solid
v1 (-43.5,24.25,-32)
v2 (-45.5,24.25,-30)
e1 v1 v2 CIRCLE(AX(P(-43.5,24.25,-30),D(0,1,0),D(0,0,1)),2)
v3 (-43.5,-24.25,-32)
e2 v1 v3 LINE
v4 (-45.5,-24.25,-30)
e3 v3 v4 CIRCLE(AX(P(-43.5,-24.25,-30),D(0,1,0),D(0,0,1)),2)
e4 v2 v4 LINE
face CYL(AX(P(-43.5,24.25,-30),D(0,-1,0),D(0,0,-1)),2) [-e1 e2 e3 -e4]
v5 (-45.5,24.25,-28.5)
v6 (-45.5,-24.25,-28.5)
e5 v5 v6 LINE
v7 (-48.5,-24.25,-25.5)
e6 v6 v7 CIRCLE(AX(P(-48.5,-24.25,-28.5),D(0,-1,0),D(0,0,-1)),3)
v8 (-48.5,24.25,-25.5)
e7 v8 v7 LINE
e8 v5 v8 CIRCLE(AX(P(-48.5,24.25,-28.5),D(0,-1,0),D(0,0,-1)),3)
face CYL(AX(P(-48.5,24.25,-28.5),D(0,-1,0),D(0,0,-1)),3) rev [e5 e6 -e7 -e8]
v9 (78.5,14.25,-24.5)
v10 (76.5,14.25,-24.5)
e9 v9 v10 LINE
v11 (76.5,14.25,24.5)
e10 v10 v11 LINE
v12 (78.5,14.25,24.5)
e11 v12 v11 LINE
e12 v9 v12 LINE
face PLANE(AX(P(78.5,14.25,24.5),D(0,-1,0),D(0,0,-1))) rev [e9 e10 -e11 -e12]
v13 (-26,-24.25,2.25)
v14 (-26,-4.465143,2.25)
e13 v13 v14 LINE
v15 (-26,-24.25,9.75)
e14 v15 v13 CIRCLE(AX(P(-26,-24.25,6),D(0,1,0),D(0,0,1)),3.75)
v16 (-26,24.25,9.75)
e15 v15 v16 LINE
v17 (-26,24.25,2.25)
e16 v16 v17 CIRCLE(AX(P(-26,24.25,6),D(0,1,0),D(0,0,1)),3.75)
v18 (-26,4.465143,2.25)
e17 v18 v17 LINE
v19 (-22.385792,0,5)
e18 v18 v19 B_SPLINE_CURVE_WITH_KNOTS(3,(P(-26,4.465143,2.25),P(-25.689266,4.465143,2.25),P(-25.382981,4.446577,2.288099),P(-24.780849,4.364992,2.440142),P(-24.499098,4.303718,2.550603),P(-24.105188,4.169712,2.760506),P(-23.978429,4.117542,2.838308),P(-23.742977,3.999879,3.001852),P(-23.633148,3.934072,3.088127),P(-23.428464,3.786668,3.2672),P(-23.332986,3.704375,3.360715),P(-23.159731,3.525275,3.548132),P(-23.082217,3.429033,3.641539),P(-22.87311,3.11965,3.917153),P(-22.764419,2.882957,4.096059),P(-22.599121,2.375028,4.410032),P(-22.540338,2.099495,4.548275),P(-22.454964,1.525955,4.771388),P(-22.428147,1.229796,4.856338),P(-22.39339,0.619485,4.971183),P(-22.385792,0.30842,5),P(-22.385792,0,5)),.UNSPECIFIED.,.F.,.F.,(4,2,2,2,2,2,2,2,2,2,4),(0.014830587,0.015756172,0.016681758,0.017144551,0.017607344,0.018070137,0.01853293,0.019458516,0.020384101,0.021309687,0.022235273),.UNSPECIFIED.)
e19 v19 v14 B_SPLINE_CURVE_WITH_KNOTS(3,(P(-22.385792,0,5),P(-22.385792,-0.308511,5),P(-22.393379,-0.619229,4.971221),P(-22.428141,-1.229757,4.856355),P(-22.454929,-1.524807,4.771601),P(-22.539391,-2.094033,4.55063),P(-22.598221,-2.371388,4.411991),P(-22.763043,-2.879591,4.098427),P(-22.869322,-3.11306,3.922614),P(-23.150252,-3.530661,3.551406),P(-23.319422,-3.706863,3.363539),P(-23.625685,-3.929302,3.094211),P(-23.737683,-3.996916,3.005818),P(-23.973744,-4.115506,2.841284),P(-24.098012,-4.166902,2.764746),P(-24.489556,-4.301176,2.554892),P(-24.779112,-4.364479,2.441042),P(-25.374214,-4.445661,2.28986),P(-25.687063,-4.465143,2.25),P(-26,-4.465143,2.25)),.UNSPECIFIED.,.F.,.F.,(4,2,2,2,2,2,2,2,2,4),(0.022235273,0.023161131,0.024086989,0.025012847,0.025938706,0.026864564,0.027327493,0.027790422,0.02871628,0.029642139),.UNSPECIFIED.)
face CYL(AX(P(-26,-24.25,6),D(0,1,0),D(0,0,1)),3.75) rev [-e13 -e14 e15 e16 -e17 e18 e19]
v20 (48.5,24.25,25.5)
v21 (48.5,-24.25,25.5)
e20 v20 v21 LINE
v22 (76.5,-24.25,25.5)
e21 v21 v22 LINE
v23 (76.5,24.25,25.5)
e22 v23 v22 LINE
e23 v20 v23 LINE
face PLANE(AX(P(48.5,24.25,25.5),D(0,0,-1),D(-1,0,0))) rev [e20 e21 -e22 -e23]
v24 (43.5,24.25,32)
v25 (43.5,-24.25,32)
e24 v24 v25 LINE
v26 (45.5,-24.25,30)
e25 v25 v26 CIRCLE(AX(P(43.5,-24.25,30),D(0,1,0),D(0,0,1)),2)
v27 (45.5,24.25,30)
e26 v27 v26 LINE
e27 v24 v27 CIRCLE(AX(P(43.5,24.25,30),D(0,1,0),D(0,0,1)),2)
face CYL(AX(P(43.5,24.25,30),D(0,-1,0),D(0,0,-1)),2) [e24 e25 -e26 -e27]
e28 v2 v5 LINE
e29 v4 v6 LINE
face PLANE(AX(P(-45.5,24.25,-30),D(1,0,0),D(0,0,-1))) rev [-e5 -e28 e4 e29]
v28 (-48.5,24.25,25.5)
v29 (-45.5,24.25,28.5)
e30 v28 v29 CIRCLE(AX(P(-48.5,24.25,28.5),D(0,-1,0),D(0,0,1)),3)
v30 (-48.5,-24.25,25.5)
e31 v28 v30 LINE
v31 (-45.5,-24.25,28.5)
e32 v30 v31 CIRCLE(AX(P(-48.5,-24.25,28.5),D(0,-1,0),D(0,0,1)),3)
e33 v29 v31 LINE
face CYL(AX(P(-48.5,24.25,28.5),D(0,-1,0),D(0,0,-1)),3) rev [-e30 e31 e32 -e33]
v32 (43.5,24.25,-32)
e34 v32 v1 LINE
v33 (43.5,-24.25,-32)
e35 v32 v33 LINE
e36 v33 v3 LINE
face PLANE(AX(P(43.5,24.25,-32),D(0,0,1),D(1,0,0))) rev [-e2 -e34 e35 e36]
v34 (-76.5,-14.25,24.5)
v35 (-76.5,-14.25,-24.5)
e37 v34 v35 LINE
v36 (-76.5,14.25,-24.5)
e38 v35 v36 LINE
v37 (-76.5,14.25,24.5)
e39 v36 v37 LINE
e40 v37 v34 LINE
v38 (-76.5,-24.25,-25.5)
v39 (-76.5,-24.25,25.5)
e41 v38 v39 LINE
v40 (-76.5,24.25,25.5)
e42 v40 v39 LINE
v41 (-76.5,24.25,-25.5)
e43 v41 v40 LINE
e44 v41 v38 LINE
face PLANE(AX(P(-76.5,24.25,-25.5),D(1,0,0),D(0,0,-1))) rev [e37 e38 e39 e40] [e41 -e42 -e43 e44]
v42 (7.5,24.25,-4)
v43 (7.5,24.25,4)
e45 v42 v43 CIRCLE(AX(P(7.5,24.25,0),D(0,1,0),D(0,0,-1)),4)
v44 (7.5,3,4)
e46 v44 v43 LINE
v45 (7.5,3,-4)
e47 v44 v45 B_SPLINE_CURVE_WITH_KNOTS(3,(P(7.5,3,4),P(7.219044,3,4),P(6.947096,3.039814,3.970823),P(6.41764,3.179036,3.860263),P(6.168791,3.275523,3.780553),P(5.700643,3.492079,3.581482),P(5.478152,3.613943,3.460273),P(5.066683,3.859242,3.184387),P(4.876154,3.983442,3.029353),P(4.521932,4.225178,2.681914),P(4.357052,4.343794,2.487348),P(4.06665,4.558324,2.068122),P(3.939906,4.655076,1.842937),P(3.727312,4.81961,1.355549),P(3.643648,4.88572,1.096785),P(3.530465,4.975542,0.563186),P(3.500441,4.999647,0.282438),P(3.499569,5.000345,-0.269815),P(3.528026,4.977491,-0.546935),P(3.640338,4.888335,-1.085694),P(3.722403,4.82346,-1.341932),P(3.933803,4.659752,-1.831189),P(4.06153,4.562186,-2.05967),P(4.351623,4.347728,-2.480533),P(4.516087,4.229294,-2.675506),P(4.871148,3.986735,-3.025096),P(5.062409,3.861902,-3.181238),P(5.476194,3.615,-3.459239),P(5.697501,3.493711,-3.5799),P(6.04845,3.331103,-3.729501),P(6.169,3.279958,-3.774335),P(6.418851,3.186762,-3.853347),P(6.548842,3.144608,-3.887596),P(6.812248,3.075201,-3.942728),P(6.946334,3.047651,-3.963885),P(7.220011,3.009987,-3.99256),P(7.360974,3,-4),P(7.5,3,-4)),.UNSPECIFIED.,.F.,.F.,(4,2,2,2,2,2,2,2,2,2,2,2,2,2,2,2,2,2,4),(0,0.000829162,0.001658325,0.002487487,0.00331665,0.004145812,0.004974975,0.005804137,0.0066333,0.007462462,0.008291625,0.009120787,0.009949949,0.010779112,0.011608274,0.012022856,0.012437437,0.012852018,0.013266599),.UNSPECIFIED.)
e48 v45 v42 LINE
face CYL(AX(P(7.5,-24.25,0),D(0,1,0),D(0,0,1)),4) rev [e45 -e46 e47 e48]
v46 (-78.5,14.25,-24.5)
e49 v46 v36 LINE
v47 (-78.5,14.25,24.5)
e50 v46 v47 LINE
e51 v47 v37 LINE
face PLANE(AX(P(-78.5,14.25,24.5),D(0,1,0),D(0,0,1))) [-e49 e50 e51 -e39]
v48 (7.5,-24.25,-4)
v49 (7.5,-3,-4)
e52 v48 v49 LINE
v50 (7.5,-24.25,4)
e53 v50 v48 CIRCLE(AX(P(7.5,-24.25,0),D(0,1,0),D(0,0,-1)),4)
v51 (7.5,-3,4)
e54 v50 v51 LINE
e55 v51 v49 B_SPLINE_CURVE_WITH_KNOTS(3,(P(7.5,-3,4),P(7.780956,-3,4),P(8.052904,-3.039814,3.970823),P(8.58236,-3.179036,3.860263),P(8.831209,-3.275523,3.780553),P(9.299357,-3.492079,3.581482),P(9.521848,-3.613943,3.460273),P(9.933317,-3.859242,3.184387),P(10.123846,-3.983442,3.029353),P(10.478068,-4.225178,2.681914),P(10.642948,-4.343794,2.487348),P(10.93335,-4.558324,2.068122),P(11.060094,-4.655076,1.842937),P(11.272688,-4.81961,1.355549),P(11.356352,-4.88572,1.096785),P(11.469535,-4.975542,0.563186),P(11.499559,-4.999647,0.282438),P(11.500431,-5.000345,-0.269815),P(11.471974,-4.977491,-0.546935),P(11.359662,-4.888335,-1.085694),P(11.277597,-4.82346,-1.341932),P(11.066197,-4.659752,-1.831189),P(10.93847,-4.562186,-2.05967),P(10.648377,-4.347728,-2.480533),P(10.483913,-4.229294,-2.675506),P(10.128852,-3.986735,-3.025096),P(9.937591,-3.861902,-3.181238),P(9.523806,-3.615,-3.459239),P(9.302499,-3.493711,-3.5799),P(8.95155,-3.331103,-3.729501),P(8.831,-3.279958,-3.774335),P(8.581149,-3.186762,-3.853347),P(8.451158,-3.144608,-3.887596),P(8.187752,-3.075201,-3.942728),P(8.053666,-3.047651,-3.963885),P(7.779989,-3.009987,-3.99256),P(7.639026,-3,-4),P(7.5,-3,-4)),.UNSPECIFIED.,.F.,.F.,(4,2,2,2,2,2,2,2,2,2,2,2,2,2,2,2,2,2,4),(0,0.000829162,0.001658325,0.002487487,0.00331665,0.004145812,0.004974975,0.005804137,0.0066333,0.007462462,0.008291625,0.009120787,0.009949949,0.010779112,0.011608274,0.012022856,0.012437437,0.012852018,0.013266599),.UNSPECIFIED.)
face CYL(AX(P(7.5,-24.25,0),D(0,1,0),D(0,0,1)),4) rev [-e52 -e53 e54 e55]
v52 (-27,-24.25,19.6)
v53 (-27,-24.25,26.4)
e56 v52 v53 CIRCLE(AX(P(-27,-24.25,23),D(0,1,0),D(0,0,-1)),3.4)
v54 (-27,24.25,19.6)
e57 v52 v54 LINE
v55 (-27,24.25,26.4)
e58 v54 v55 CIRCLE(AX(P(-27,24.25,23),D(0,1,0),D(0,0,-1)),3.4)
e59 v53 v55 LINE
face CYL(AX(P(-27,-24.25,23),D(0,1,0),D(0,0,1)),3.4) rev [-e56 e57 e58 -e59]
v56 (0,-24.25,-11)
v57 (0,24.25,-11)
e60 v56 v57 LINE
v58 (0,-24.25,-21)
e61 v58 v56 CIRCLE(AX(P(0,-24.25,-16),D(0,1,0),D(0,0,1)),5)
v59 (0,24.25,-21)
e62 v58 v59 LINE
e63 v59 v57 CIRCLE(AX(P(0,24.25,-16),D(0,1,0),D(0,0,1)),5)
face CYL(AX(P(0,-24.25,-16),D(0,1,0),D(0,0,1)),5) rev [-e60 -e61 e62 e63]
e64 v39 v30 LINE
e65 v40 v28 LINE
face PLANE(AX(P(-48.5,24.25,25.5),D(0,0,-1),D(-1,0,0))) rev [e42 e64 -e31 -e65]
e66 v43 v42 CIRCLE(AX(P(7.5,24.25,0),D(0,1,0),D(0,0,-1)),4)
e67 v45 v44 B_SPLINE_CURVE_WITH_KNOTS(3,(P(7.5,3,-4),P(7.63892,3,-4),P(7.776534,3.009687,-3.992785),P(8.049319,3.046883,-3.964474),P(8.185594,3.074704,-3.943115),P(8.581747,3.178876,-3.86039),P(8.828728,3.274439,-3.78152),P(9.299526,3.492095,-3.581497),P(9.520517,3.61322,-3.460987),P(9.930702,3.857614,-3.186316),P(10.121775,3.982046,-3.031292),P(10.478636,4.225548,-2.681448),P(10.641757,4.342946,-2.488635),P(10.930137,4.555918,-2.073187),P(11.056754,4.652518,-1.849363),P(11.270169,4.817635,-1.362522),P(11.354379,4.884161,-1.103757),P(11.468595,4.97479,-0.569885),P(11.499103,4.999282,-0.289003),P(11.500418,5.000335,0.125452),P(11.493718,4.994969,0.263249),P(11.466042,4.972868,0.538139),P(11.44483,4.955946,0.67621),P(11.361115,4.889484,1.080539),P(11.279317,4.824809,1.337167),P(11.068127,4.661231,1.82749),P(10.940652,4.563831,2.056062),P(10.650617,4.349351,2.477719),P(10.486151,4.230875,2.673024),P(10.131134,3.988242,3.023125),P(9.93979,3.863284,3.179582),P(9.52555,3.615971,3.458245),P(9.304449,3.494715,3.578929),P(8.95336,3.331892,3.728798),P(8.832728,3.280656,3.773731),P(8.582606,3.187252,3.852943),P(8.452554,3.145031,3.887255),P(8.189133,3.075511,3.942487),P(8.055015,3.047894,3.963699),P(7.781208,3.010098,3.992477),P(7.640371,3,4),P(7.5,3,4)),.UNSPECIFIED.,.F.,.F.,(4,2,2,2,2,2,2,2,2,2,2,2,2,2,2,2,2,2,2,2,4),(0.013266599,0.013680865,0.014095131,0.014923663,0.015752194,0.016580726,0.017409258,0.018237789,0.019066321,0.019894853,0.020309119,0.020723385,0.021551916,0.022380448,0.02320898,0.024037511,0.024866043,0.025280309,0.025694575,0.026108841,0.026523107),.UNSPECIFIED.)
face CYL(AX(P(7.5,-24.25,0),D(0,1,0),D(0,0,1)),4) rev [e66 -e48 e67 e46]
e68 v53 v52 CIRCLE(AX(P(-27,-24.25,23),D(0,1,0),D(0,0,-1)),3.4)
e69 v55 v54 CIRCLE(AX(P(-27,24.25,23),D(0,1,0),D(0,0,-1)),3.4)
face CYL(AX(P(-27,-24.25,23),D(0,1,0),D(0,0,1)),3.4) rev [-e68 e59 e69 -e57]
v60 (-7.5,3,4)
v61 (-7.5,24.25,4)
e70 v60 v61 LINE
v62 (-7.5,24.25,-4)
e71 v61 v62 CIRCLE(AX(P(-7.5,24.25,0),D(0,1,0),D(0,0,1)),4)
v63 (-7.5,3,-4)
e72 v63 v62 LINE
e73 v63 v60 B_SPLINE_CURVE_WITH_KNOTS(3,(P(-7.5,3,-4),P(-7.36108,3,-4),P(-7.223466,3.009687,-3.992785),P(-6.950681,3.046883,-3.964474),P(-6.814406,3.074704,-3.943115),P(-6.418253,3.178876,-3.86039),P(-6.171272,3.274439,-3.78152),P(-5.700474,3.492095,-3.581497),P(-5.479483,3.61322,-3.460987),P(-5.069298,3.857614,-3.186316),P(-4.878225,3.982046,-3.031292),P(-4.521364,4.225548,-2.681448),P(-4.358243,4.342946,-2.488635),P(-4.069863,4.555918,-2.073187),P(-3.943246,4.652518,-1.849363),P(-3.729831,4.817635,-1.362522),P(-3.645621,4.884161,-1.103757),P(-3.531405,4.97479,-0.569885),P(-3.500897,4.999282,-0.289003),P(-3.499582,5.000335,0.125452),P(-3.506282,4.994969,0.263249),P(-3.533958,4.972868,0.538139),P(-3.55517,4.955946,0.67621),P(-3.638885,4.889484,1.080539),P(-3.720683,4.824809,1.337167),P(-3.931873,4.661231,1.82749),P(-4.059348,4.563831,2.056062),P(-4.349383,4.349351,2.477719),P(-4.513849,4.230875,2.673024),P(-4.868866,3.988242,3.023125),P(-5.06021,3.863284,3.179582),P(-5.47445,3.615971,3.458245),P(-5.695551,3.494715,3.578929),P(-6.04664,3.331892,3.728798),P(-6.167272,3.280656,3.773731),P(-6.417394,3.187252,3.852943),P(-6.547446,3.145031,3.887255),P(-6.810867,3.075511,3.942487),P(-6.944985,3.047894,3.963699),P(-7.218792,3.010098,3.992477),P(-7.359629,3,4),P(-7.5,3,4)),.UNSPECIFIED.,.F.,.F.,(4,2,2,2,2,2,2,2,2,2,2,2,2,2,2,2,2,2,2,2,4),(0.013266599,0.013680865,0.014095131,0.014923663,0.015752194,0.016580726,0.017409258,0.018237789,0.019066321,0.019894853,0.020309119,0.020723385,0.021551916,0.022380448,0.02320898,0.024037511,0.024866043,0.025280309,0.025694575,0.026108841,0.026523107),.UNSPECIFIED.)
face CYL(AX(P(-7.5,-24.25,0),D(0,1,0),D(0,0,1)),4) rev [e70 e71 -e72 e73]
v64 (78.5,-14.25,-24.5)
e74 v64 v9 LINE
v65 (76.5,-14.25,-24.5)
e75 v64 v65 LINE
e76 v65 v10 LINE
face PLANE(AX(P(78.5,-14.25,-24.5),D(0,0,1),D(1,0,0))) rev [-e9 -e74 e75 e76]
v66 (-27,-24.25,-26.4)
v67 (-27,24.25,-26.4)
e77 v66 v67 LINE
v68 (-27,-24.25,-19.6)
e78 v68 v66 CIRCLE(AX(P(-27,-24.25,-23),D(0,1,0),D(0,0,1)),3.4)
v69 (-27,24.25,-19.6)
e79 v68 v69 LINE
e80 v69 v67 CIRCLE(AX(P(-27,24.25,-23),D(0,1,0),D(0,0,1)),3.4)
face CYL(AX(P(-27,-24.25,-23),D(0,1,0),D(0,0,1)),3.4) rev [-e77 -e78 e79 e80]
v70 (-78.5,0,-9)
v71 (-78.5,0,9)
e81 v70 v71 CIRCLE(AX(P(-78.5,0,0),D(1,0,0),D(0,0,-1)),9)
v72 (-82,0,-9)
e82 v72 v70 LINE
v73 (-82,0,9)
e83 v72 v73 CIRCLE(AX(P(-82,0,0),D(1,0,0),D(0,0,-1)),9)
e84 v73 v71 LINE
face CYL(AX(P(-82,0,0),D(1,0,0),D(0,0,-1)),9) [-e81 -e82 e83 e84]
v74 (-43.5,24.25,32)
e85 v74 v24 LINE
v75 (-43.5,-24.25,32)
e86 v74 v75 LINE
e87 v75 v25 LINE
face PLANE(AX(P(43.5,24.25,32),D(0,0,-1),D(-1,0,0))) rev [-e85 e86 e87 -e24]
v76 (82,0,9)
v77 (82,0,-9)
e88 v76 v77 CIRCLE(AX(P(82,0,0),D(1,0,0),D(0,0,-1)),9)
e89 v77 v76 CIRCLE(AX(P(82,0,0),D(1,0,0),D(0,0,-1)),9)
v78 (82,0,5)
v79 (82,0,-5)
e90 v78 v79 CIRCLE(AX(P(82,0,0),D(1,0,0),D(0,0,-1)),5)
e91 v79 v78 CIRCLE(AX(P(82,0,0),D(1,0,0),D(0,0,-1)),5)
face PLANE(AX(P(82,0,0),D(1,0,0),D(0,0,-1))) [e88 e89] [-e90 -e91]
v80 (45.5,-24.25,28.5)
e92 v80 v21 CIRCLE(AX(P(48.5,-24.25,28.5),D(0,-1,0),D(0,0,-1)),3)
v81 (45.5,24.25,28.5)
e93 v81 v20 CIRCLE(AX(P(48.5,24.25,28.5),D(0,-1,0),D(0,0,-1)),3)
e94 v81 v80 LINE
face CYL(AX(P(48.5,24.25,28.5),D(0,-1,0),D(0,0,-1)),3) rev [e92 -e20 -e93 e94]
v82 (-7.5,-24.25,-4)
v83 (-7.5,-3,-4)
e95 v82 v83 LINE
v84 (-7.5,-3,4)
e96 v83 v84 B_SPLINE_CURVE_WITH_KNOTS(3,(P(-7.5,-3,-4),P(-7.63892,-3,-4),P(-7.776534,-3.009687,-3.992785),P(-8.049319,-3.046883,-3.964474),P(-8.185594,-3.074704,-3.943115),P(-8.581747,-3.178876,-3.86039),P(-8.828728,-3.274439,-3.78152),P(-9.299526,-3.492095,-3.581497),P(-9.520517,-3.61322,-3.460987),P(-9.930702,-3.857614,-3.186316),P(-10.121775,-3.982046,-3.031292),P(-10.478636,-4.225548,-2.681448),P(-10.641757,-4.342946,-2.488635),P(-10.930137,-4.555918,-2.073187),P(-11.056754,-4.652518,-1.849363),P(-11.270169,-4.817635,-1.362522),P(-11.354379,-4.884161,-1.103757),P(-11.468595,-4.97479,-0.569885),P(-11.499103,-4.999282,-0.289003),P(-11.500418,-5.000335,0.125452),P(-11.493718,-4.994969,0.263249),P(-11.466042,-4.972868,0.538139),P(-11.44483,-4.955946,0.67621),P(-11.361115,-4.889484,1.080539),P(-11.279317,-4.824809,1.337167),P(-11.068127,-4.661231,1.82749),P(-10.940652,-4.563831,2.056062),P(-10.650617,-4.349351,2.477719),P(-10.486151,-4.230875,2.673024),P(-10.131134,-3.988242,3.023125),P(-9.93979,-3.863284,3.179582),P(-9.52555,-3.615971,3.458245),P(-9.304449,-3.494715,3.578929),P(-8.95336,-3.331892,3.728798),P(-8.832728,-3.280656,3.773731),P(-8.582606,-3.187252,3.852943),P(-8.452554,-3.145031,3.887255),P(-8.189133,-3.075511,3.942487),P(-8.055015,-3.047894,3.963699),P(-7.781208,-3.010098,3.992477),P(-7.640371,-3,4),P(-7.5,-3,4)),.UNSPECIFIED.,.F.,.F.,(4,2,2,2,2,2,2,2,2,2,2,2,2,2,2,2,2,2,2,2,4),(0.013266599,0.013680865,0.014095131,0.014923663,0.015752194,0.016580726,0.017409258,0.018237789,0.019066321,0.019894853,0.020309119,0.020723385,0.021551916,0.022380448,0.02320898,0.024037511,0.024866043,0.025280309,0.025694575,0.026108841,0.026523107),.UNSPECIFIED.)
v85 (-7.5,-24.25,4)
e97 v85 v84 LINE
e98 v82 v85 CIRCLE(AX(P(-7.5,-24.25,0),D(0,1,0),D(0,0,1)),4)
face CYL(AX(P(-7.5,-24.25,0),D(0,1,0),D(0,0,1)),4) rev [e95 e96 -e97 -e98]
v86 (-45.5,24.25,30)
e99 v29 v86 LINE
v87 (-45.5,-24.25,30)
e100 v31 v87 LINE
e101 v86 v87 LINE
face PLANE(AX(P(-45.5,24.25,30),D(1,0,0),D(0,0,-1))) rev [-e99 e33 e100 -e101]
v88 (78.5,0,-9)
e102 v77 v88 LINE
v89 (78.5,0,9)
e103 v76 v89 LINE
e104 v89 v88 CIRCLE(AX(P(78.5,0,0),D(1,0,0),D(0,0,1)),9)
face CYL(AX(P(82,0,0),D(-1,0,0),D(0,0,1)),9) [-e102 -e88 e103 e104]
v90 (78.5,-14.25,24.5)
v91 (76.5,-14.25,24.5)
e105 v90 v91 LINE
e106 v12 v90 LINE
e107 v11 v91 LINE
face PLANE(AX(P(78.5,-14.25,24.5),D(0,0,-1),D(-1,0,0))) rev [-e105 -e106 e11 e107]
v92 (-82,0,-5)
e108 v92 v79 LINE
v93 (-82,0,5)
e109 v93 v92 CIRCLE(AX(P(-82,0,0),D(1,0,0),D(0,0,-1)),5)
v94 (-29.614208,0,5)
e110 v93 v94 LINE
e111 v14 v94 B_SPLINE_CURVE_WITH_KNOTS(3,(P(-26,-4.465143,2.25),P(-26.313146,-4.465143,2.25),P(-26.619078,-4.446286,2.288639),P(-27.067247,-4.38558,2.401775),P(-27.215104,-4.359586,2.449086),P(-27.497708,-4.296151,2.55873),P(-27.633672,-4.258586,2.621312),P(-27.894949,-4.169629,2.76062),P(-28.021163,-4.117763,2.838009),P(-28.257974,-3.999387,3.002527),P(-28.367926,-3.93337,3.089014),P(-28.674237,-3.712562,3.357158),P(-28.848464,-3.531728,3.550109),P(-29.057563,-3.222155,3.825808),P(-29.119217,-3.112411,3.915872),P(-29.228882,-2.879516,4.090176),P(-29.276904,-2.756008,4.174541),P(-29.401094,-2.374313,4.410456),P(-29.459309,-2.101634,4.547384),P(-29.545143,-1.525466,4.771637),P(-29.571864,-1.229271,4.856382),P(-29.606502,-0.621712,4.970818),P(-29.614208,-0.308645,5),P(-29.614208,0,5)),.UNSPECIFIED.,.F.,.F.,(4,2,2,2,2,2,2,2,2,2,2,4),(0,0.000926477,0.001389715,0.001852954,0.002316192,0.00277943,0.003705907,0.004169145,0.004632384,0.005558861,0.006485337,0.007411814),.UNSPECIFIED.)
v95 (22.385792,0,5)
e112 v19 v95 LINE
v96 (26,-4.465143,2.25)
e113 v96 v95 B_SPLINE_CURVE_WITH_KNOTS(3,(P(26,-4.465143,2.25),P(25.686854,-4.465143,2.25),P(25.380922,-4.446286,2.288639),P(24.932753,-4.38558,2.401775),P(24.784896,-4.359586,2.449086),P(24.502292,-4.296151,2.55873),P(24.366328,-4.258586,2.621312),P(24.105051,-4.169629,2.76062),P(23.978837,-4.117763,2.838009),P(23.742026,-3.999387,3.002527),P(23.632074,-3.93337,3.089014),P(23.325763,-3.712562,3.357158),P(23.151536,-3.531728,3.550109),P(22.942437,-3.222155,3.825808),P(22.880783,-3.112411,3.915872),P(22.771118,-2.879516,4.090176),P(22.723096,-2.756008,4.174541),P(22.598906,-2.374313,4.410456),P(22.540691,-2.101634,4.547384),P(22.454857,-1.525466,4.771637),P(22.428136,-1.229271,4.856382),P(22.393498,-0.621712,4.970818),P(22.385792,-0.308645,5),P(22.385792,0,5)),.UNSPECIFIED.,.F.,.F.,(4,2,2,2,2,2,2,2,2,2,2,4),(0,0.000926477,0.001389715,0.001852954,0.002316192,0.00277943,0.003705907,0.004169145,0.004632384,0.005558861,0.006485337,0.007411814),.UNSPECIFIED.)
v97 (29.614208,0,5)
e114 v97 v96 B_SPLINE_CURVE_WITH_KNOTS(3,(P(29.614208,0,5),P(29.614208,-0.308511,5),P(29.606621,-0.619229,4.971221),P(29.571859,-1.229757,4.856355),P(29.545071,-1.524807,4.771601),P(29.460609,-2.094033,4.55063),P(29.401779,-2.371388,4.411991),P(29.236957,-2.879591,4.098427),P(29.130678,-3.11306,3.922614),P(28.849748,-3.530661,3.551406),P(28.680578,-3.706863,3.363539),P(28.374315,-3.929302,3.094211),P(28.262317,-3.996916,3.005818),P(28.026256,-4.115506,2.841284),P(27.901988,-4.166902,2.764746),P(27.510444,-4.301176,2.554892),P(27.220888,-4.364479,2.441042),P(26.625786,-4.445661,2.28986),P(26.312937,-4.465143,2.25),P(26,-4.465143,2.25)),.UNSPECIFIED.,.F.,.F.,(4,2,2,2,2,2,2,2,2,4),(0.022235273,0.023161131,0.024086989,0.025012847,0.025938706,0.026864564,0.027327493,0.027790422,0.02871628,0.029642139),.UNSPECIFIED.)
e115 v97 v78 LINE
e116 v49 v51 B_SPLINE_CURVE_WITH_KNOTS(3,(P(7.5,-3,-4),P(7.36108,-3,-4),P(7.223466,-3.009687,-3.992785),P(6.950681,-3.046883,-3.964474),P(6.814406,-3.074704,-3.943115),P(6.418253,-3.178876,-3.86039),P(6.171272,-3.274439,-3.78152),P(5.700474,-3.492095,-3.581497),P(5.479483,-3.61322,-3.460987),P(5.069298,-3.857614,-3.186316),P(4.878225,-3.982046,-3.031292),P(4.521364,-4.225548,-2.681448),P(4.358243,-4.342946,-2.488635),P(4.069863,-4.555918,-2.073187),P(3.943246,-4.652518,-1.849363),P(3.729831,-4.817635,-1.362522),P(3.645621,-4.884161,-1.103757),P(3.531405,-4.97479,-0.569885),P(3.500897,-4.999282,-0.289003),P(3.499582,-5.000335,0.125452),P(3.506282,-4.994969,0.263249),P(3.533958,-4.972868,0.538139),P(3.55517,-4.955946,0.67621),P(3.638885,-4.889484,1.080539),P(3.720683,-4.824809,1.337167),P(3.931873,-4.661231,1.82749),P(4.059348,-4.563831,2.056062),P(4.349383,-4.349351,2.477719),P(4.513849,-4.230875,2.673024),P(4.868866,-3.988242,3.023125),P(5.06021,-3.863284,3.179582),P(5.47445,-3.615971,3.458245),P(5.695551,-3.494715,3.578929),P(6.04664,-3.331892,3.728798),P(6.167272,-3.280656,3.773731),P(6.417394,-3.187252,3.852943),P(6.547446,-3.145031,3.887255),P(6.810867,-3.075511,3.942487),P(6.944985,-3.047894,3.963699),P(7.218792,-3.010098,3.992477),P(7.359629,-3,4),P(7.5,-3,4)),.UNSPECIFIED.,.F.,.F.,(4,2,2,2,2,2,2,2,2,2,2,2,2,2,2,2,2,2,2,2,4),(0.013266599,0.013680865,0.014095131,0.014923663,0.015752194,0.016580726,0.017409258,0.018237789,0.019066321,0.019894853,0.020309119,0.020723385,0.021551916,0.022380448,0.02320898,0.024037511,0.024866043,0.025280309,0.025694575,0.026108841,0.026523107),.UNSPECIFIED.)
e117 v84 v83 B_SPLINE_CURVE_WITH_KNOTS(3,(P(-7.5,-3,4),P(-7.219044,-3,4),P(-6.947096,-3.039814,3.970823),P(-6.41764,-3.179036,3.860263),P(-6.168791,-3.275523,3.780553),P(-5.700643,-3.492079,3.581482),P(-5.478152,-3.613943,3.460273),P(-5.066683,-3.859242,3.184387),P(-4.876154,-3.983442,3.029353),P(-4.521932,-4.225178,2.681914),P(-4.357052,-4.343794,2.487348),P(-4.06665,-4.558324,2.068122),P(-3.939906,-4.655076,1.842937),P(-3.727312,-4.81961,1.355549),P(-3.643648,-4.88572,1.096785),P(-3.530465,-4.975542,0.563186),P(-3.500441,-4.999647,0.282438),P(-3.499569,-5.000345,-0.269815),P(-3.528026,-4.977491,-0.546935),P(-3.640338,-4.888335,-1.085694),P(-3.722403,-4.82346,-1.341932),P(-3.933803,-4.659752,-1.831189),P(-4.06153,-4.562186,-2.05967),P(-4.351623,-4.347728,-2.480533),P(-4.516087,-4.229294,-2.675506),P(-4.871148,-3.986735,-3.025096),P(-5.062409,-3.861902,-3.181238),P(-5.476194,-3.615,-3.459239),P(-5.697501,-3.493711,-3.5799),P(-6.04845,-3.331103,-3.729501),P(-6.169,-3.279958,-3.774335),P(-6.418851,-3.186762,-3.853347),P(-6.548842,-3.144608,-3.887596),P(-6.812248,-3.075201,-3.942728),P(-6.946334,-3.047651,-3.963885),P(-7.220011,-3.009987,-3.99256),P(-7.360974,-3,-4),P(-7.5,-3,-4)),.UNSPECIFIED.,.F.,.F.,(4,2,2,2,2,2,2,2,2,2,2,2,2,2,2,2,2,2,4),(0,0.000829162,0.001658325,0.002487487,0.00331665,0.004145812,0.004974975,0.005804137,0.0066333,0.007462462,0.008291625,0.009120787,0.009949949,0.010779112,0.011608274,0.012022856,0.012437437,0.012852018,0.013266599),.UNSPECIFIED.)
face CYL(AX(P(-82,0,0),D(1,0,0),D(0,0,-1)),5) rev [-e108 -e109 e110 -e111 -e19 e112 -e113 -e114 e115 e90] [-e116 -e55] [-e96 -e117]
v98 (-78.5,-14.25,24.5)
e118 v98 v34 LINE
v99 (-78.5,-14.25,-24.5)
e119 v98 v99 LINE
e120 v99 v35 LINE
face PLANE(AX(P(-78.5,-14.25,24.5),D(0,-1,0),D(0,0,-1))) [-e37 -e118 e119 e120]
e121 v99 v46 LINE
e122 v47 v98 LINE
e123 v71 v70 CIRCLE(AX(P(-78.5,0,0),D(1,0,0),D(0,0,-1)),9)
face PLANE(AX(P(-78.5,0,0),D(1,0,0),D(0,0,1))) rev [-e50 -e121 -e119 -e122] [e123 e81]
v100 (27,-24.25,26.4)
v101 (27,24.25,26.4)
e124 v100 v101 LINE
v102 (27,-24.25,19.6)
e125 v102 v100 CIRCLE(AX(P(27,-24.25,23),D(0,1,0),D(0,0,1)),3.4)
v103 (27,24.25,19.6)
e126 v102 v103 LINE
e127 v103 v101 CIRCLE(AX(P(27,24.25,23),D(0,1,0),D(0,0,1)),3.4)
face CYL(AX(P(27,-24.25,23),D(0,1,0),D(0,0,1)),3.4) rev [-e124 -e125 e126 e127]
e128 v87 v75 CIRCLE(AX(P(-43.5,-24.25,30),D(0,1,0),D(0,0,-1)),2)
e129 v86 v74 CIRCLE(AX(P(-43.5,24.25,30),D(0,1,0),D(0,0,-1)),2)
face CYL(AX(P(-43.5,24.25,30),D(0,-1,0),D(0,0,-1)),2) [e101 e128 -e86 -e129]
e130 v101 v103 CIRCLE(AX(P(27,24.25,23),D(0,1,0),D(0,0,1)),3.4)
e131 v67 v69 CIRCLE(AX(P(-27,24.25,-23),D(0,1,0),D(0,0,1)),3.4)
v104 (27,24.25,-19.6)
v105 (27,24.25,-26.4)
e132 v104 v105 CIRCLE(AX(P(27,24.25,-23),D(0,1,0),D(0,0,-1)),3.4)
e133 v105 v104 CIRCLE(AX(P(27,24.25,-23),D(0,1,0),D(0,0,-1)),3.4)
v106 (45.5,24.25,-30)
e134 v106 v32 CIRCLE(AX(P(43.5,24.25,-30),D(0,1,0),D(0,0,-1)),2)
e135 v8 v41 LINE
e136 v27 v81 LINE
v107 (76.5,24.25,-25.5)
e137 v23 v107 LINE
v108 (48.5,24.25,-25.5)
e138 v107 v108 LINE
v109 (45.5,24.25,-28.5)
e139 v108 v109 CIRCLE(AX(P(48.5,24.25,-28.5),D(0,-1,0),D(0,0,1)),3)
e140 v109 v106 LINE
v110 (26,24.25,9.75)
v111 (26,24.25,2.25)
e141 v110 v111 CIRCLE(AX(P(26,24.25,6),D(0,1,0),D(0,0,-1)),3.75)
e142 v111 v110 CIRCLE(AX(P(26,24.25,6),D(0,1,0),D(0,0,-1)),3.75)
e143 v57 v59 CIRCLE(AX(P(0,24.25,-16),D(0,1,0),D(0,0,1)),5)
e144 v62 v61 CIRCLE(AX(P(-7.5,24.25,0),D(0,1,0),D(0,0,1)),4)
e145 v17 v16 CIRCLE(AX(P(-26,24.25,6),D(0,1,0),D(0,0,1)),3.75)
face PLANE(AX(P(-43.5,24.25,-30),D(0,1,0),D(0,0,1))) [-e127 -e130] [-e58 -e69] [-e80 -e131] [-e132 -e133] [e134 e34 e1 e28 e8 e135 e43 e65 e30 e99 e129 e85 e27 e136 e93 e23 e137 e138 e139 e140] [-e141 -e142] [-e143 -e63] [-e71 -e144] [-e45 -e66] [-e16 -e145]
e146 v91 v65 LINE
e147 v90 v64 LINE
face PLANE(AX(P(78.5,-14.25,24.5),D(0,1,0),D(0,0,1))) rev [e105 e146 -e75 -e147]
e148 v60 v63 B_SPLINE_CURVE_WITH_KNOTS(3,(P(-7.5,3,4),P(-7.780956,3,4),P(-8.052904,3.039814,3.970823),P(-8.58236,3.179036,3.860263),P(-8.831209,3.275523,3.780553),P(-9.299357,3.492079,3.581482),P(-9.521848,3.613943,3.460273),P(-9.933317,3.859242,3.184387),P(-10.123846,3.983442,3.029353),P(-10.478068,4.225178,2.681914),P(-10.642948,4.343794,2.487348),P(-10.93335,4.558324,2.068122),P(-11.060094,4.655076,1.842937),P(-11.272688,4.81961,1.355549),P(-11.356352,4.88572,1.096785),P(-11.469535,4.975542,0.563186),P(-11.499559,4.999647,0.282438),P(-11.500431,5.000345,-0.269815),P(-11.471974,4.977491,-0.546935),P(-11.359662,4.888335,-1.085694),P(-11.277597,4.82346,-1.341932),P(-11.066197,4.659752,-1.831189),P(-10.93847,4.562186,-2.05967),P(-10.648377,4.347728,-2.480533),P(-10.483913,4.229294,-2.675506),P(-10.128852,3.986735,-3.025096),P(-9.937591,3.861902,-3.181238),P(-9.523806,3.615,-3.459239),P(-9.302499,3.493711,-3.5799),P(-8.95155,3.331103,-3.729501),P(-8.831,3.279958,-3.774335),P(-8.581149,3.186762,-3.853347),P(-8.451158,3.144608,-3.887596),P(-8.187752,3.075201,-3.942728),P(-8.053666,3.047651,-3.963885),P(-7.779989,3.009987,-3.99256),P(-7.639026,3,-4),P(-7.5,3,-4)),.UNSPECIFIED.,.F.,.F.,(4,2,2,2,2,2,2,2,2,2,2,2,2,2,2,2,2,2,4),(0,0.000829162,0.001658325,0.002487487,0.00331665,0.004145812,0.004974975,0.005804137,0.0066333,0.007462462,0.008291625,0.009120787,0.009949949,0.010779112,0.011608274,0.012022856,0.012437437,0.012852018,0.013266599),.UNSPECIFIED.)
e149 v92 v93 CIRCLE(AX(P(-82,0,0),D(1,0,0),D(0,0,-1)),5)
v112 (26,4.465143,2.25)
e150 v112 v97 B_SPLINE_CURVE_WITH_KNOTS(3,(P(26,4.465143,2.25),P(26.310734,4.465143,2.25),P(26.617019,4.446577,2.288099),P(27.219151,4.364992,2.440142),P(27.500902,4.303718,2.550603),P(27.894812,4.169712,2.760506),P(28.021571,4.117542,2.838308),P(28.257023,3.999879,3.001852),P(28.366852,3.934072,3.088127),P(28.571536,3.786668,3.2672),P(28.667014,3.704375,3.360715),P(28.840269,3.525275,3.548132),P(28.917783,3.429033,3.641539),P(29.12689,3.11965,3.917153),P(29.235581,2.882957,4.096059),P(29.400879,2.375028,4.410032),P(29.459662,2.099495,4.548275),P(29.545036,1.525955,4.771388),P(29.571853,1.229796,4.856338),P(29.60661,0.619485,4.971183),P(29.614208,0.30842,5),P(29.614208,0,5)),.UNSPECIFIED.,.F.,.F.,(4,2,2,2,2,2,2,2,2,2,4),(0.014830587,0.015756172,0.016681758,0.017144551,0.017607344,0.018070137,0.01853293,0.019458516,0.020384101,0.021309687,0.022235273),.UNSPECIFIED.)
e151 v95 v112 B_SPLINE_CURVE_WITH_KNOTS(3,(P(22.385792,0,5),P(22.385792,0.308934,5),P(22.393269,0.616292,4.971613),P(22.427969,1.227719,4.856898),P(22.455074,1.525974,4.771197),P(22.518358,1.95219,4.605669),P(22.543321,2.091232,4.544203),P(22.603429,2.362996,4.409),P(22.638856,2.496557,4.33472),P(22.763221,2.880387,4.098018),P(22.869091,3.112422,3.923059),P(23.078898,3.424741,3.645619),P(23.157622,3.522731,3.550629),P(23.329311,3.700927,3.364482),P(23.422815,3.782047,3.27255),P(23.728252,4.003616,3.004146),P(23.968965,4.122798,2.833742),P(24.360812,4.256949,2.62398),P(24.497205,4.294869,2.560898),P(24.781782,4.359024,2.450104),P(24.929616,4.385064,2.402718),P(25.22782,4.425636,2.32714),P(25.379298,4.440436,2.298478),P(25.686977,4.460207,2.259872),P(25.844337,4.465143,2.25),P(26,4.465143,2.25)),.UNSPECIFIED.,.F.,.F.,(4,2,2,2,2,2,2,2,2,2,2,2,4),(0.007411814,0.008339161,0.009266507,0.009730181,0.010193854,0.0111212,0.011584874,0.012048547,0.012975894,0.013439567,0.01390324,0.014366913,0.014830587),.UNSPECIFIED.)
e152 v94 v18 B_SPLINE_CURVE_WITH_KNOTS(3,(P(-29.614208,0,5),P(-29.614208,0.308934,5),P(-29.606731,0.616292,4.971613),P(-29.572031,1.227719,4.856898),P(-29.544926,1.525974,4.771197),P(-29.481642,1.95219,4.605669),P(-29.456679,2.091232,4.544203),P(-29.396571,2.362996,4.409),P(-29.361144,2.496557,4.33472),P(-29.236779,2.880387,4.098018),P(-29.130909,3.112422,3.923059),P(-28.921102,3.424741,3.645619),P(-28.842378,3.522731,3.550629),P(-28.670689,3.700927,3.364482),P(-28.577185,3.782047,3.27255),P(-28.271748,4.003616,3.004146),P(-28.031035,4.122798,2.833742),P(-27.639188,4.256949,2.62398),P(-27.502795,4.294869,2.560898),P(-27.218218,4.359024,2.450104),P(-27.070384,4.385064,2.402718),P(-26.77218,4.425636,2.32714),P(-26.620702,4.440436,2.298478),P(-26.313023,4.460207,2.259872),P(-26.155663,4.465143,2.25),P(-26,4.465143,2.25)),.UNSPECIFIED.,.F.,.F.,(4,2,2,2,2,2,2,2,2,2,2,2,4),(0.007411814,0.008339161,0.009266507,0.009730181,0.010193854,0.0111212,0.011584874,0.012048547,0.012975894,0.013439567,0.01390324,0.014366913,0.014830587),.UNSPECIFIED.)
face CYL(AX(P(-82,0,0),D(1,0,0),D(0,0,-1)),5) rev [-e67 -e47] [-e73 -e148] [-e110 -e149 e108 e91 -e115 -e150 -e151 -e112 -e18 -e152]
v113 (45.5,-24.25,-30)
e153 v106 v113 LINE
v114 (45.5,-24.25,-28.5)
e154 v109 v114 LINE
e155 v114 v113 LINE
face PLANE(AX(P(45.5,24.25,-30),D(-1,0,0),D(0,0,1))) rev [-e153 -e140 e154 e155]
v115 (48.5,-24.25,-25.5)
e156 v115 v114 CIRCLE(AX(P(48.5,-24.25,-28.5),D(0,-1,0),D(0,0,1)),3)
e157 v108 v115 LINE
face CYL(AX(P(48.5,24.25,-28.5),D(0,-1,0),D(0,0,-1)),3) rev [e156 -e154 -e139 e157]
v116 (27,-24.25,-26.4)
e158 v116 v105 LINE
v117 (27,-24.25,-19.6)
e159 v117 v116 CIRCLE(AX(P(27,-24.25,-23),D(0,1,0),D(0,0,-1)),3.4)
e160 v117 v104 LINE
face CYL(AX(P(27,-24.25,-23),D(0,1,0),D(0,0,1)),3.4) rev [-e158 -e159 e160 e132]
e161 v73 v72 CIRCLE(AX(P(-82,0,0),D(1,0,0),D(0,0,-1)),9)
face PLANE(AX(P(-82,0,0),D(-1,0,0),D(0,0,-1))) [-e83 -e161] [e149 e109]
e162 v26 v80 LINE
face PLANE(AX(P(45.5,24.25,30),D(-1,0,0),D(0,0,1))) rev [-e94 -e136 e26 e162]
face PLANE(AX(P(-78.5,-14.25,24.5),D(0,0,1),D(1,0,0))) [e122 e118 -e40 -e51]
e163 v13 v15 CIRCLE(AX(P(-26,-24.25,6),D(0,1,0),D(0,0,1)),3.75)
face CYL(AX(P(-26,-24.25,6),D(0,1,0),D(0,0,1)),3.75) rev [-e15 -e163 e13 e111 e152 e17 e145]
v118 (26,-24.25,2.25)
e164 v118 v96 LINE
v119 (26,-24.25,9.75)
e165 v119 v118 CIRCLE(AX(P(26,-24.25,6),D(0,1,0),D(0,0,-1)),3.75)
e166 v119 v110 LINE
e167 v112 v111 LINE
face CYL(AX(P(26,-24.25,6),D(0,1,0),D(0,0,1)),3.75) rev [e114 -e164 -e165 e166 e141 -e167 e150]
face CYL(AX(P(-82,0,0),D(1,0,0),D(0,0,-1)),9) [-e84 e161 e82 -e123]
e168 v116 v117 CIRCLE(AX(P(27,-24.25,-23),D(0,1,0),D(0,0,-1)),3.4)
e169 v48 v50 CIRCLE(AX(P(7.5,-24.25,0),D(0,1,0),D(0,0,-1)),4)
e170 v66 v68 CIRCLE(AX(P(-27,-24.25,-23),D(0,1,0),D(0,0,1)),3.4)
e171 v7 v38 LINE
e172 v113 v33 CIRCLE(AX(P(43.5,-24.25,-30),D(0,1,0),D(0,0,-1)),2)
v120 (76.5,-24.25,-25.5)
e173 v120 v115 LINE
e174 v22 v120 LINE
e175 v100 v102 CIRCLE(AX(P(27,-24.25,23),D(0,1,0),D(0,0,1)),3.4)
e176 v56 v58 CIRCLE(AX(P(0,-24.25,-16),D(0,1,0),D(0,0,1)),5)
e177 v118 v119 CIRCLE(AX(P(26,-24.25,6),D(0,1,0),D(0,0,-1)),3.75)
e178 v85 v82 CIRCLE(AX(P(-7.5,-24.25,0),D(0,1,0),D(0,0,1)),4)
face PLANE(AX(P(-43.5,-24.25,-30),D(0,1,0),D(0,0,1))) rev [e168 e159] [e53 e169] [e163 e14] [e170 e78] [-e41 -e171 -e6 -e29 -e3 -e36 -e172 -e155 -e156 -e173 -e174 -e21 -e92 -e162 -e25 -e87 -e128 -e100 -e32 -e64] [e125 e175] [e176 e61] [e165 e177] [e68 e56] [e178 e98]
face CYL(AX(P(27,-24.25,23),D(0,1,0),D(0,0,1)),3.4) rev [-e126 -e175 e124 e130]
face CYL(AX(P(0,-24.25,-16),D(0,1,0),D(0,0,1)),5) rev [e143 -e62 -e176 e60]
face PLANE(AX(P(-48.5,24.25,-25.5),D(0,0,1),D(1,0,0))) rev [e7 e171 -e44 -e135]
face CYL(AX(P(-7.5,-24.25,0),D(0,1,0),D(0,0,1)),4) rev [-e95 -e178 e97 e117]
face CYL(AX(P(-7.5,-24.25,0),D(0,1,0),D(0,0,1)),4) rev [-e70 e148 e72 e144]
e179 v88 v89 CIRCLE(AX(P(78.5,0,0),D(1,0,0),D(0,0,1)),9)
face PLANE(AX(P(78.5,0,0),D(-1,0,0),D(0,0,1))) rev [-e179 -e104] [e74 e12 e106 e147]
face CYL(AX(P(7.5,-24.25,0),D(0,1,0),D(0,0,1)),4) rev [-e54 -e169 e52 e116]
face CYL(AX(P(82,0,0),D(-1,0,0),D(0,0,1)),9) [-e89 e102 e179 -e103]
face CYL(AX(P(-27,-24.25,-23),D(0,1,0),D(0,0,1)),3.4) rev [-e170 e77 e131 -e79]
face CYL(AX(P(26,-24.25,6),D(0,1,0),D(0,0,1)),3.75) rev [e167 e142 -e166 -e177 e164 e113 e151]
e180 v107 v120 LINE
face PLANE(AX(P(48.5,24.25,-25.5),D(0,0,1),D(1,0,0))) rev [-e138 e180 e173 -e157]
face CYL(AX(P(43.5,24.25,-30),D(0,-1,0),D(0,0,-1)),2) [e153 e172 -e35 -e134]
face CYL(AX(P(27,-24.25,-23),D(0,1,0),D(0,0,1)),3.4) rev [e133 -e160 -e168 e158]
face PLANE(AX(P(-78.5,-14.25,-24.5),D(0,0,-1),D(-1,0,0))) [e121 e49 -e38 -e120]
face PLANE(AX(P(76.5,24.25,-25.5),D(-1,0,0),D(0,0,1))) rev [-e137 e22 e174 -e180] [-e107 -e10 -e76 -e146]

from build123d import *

# Parameters (mm, degrees)
BOSS_EXTRUDE_1_DEPTH = 24.25
SKETCH_2_W           = 49
SKETCH_2_H           = 28.5
SKETCH_2_R           = 3.024345666
BOSS_EXTRUDE_2_DEPTH = 2
SKETCH_3_R           = 9
BOSS_EXTRUDE_3_DEPTH = 5.5
SKETCH_4_R           = 3.4
SKETCH_4_R_2         = 5
SKETCH_4_R_3         = 4
SKETCH_4_R_4         = 3.75
CUT_EXTRUDE_1_DEPTH  = 101.5
SKETCH_5_R           = 5
CUT_EXTRUDE_2_DEPTH  = 169.843307537


with BuildPart() as part:
    # Sketch 1 → Boss-Extrude 1 (new, symmetric)
    with BuildSketch(Plane(origin=(0, 0, 0), x_dir=(1, 0, 0), z_dir=(0, 1, 0))):
        with BuildLine():
            Line((43.5, 32), (-43.5, 32))
            ThreePointArc((-43.5, 32), (-44.914213562, 31.414213562), (-45.5, 30))
            Line((-45.5, 30), (-45.5, 28.5))
            ThreePointArc((-45.5, 28.5), (-46.378679656, 26.378679656), (-48.5, 25.5))
            Line((-48.5, 25.5), (-76.5, 25.5))
            Line((-76.5, 25.5), (-76.5, -25.5))
            Line((-76.5, -25.5), (-48.5, -25.5))
            ThreePointArc((-48.5, -25.5), (-46.378679656, -26.378679656), (-45.5, -28.5))
            Line((-45.5, -28.5), (-45.5, -30))
            ThreePointArc((-45.5, -30), (-44.914213562, -31.414213562), (-43.5, -32))
            Line((-43.5, -32), (43.5, -32))
            ThreePointArc((43.5, -32), (44.914213562, -31.414213562), (45.5, -30))
            Line((45.5, -30), (45.5, -28.5))
            ThreePointArc((45.5, -28.5), (46.378679656, -26.378679656), (48.5, -25.5))
            Line((48.5, -25.5), (76.5, -25.5))
            Line((76.5, -25.5), (76.5, 25.5))
            Line((76.5, 25.5), (48.5, 25.5))
            ThreePointArc((48.5, 25.5), (46.378679656, 26.378679656), (45.5, 28.5))
            Line((45.5, 28.5), (45.5, 30))
            ThreePointArc((45.5, 30), (44.914213562, 31.414213562), (43.5, 32))
        make_face()
    extrude(amount=BOSS_EXTRUDE_1_DEPTH, both=True)

    # Sketch 2 → Boss-Extrude 2 (add)
    with BuildSketch(Plane(origin=(76.5, 0, 0), x_dir=(0, 0, -1), z_dir=(1, 0, 0))):
        Rectangle(SKETCH_2_W, SKETCH_2_H)
        Circle(SKETCH_2_R, mode=Mode.SUBTRACT)
    boss_extrude_2 = extrude(amount=BOSS_EXTRUDE_2_DEPTH)

    # Sketch 3 → Boss-Extrude 3 (add)
    with BuildSketch(Plane(origin=(76.5, 0, 0), x_dir=(0, 0, -1), z_dir=(1, 0, 0))):
        with Locations(Location((0, 0, 0), (0, 0, 180))):
            Circle(SKETCH_3_R)
    boss_extrude_3 = extrude(amount=BOSS_EXTRUDE_3_DEPTH)

    # Mirror 1: Boss-Extrude 2, Boss-Extrude 3 across plane
    add(boss_extrude_2.mirror(Plane(origin=(0, 0, 0), x_dir=(0, 0, 1), z_dir=(1, 0, 0))))
    add(boss_extrude_3.mirror(Plane(origin=(0, 0, 0), x_dir=(0, 0, 1), z_dir=(1, 0, 0))))

    # Sketch 4 → Cut-Extrude 1 (cut, through all)
    with BuildSketch(Plane(origin=(0, 24.25, 0), x_dir=(1, 0, 0), z_dir=(0, 1, 0))):
        with Locations(Location((-27, 23, 0), (0, 0, 270))):
            Circle(SKETCH_4_R)
        with Locations(Location((0, 16, 0), (0, 0, 270))):
            Circle(SKETCH_4_R_2)
        with Locations(Location((-7.5, 0, 0), (0, 0, 270))):
            Circle(SKETCH_4_R_3)
        with Locations(Location((-26, -6, 0), (0, 0, 270))):
            Circle(SKETCH_4_R_4)
        with Locations(Location((-27, -23, 0), (0, 0, 270))):
            Circle(SKETCH_4_R)
        with Locations(Location((7.5, 0, 0), (0, 0, 270))):
            Circle(SKETCH_4_R_3)
        with Locations(Location((27, -23, 0), (0, 0, 270))):
            Circle(SKETCH_4_R)
        with Locations(Location((26, -6, 0), (0, 0, 270))):
            Circle(SKETCH_4_R_4)
        with Locations(Location((27, 23, 0), (0, 0, 270))):
            Circle(SKETCH_4_R)
    extrude(amount=-CUT_EXTRUDE_1_DEPTH, mode=Mode.SUBTRACT)

    # Sketch 5 → Cut-Extrude 2 (cut, through all)
    with BuildSketch(Plane(origin=(82, 0, 0), x_dir=(0, 0, -1), z_dir=(1, 0, 0))):
        Circle(SKETCH_5_R)
    extrude(amount=-CUT_EXTRUDE_2_DEPTH, mode=Mode.SUBTRACT)


solid = part.part
